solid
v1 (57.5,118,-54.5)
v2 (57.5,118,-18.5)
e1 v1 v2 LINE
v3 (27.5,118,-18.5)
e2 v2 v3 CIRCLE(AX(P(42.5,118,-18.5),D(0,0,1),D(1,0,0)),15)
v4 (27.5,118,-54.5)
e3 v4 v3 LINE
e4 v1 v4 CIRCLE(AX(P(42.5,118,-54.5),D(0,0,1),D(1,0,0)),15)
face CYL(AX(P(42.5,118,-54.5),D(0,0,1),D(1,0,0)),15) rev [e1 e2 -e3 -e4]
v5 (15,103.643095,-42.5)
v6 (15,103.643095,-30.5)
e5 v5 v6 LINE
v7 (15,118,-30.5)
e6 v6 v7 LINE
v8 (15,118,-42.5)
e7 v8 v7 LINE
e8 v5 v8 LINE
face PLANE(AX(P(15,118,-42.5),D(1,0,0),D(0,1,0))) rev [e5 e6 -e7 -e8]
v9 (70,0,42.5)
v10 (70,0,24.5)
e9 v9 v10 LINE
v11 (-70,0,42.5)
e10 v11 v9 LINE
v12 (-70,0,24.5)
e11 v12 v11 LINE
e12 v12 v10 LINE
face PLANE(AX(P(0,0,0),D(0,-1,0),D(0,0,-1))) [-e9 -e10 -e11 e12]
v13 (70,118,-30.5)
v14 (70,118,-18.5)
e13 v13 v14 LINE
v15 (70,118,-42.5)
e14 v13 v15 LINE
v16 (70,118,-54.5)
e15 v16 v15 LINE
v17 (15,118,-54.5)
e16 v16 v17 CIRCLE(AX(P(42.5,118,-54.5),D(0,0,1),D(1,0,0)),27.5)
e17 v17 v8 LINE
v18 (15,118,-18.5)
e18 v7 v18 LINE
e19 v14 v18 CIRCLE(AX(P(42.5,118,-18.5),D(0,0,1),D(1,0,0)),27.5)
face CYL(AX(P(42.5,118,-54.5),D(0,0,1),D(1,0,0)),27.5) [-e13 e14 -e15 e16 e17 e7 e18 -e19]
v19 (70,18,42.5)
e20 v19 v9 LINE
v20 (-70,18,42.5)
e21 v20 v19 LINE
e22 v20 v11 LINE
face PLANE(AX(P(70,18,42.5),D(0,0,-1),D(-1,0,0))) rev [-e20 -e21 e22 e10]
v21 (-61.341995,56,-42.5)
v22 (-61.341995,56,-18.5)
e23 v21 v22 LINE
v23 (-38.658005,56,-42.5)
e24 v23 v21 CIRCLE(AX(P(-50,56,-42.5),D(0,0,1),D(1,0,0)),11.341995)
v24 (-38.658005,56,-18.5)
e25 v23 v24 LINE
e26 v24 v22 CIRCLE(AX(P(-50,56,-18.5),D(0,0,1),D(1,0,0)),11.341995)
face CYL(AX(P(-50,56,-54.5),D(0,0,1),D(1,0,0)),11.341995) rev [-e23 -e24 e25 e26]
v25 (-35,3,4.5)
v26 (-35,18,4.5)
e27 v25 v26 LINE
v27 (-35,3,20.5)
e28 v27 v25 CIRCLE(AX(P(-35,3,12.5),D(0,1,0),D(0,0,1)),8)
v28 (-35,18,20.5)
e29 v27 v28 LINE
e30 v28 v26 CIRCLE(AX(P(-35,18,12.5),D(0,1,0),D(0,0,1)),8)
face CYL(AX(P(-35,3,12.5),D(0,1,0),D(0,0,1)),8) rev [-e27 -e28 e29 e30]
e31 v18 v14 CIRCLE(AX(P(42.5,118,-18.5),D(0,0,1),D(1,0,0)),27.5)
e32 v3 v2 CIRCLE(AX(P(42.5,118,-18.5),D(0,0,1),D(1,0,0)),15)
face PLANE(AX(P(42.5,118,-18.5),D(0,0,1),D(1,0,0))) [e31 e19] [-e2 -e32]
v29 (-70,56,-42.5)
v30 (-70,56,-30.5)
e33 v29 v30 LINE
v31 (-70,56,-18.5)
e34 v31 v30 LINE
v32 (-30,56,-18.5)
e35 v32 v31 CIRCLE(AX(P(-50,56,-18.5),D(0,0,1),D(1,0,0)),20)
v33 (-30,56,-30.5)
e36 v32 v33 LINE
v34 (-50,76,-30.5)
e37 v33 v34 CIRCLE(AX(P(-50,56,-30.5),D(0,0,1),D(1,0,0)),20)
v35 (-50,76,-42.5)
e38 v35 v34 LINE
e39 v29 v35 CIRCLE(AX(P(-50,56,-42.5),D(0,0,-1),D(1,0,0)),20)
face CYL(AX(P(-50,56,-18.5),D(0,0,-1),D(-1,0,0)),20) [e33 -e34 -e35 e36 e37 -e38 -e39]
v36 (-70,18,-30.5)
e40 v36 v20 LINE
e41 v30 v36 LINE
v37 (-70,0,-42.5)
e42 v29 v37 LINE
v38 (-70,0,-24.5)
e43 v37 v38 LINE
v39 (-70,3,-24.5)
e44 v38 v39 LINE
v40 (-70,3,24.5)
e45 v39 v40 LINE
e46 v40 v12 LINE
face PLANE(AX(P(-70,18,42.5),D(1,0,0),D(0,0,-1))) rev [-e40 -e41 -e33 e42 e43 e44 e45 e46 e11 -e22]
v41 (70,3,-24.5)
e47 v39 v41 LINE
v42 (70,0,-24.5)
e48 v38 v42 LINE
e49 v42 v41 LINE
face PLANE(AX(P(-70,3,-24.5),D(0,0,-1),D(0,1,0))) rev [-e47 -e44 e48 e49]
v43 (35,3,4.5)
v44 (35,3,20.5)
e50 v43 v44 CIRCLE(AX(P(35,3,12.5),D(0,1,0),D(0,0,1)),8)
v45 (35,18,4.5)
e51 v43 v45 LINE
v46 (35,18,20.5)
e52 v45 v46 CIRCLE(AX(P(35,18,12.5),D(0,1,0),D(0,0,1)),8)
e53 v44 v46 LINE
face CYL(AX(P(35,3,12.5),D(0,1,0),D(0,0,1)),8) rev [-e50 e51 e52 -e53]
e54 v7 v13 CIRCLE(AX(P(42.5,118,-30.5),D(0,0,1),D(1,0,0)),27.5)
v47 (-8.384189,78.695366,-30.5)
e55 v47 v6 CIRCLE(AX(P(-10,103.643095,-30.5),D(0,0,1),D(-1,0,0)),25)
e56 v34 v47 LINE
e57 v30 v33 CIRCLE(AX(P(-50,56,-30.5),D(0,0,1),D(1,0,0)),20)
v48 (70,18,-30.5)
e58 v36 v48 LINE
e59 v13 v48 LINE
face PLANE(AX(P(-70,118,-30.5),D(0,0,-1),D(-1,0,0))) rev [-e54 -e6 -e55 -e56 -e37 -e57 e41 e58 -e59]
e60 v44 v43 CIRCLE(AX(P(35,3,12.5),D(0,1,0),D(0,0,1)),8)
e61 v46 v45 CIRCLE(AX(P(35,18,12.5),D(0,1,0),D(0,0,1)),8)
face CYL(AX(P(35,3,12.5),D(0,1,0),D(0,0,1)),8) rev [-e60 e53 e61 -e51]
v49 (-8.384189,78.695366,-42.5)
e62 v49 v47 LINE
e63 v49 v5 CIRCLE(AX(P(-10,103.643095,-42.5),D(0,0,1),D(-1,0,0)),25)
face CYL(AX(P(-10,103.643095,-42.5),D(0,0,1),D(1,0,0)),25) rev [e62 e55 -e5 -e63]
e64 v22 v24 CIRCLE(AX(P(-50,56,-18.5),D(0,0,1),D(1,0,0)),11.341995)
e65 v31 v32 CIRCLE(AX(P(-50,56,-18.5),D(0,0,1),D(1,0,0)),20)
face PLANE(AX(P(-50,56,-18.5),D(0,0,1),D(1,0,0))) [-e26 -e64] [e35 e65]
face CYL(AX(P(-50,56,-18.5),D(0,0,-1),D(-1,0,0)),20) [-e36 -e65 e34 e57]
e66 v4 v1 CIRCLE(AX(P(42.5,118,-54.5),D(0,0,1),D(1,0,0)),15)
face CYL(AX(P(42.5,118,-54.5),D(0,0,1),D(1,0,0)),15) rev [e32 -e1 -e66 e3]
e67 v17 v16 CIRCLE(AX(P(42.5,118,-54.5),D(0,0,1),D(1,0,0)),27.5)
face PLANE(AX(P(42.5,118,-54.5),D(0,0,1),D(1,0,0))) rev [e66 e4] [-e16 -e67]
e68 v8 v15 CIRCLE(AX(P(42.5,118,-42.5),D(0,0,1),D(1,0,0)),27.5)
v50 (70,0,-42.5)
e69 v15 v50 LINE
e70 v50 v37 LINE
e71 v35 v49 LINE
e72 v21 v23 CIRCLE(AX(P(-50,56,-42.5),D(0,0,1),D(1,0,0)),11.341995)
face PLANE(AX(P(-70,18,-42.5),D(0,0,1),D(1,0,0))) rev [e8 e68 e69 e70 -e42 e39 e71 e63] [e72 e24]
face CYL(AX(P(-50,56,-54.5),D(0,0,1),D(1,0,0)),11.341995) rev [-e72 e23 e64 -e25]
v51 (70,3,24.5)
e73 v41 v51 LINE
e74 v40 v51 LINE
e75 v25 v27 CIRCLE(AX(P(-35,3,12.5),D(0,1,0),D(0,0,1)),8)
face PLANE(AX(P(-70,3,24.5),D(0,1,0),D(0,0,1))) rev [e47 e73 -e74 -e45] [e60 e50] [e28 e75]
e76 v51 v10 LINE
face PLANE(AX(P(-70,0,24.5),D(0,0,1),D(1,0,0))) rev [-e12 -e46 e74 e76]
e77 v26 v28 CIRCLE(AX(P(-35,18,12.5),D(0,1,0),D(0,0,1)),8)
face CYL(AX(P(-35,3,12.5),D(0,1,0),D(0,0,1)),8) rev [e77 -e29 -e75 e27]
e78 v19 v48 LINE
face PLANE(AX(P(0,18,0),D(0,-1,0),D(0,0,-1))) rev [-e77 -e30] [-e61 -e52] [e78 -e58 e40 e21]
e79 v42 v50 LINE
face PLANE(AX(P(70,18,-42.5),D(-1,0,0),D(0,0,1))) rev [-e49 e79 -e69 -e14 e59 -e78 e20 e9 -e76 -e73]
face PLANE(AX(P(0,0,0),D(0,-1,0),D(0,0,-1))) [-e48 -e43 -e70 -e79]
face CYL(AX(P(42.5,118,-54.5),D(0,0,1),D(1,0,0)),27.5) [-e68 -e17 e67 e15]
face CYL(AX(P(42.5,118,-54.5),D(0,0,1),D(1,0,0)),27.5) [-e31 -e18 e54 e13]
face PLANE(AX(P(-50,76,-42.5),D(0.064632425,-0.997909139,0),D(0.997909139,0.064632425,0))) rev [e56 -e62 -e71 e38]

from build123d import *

# Parameters (mm, degrees)
BASE_PLATE_SKETCH_W              = 140
BASE_PLATE_SKETCH_H              = 85
BASE_PLATE_85X140X18_DEPTH       = 18
UNDERSIDE_GROOVE_SKETCH_W        = 49
UNDERSIDE_GROOVE_SKETCH_H        = 3
UNDERSIDE_GROOVE_DEPTH           = 140
UPRIGHT_WALL_SKETCH_W            = 140
UPRIGHT_WALL_SKETCH_H            = 12
UPRIGHT_WALL_DEPTH               = 100
SMALL_LUG_40_SKETCH_R            = 20
SMALL_LUG_40_DEPTH               = 12
LARGE_LUG_55_SKETCH_R            = 27.5
LARGE_LUG_55_DEPTH               = 24
LARGE_START                      = 12
LARGE_LUG_EXTENSION_SKETCH_R     = 27.5
LARGE_LUG_EXTENSION_DEPTH        = 12
LUG_START                        = -12
LUG_RELIEF_CUT_DEPTH             = 12
LARGE_LUG_BORE_30_SKETCH_R       = 15
LARGE_LUG_BORE_30_DEPTH          = 36
SMALL_LUG_BORE_SKETCH_R          = 11.34199473
SMALL_LUG_BORE_DEPTH             = 36
BASE_MOUNTING_HOLE_1_16_SKETCH_R = 8
BASE_MOUNTING_HOLE_1_16_DEPTH    = 15
BASE_MOUNTING_HOLE_2_16_SKETCH_R = 8
BASE_MOUNTING_HOLE_2_16_DEPTH    = 15


with BuildPart() as part:
    # Base Plate Sketch → Base Plate 85x140x18 (new body)
    with BuildSketch(Plane(origin=(0, 0, 0), x_dir=(1, 0, 0), z_dir=(0, 1, 0))):
        Rectangle(BASE_PLATE_SKETCH_W, BASE_PLATE_SKETCH_H)
    extrude(amount=BASE_PLATE_85X140X18_DEPTH)

    # Underside Groove Sketch → Underside Groove (cut)
    with BuildSketch(Plane(origin=(70, 0, 0), x_dir=(0, 0, -1), z_dir=(1, 0, 0))):
        with Locations((0, 1.5)):
            Rectangle(UNDERSIDE_GROOVE_SKETCH_W, UNDERSIDE_GROOVE_SKETCH_H)
    extrude(amount=-UNDERSIDE_GROOVE_DEPTH, mode=Mode.SUBTRACT)

    # Upright Wall Sketch → Upright Wall (add)
    with BuildSketch(Plane(origin=(0, 18, 0), x_dir=(1, 0, 0), z_dir=(0, 1, 0))):
        with Locations((0, 36.5)):
            Rectangle(UPRIGHT_WALL_SKETCH_W, UPRIGHT_WALL_SKETCH_H)
    extrude(amount=UPRIGHT_WALL_DEPTH)

    # Small Lug Ø40 Sketch → Small Lug Ø40 (add)
    with BuildSketch(Plane.XY.offset(-30.5)):
        with Locations(Location((-50, 56, 0), (0, 0, 180))):
            Circle(SMALL_LUG_40_SKETCH_R)
    extrude(amount=SMALL_LUG_40_DEPTH)

    # Large Lug Ø55 Sketch → Large Lug Ø55 (add)
    with BuildSketch(Plane.XY.offset(-30.5)):
        with Locations((42.5, 118)):
            Circle(LARGE_LUG_55_SKETCH_R)
    extrude(amount=-LARGE_LUG_55_DEPTH)

    # Large Lug Extension Sketch → Large Lug Extension (add)
    with BuildSketch(Plane.XY.offset(-30.5).offset(LARGE_START)):
        with Locations((42.5, 118)):
            Circle(LARGE_LUG_EXTENSION_SKETCH_R)
    extrude(amount=-LARGE_LUG_EXTENSION_DEPTH)

    # Lug Relief Cut Sketch → Lug Relief Cut (cut)
    with BuildSketch(Plane.XY.offset(-30.5).offset(LUG_START)):
        with BuildLine():
            Line((15, 118), (15, 103.64309486))
            ThreePointArc((15, 103.64309486), (8.240000897, 86.546242306), (-8.384189381, 78.695366386))
            Line((-8.384189381, 78.695366386), (-50, 76))
            ThreePointArc((-50, 76), (-64.142135624, 70.142135624), (-70, 56))
            Line((-70, 56), (-70, 118))
            Line((-70, 118), (15, 118))
        make_face()
    extrude(amount=LUG_RELIEF_CUT_DEPTH, mode=Mode.SUBTRACT)

    # Large Lug Bore Ø30 Sketch → Large Lug Bore Ø30 (cut)
    with BuildSketch(Plane.XY.offset(-18.5)):
        with Locations((42.5, 118)):
            Circle(LARGE_LUG_BORE_30_SKETCH_R)
    extrude(amount=-LARGE_LUG_BORE_30_DEPTH, mode=Mode.SUBTRACT)

    # Small Lug Bore Sketch → Small Lug Bore (cut)
    with BuildSketch(Plane.XY.offset(-18.5)):
        with Locations((-50, 56)):
            Circle(SMALL_LUG_BORE_SKETCH_R)
    extrude(amount=-SMALL_LUG_BORE_DEPTH, mode=Mode.SUBTRACT)

    # Base Mounting Hole 1 Ø16 Sketch → Base Mounting Hole 1 Ø16 (cut)
    with BuildSketch(Plane(origin=(0, 18, 0), x_dir=(1, 0, 0), z_dir=(0, 1, 0))):
        with Locations(Location((-35, -12.5, 0), (0, 0, 270))):
            Circle(BASE_MOUNTING_HOLE_1_16_SKETCH_R)
    extrude(amount=-BASE_MOUNTING_HOLE_1_16_DEPTH, mode=Mode.SUBTRACT)

    # Base Mounting Hole 2 Ø16 Sketch → Base Mounting Hole 2 Ø16 (cut)
    with BuildSketch(Plane(origin=(0, 18, 0), x_dir=(1, 0, 0), z_dir=(0, 1, 0))):
        with Locations(Location((35, -12.5, 0), (0, 0, 270))):
            Circle(BASE_MOUNTING_HOLE_2_16_SKETCH_R)
    extrude(amount=-BASE_MOUNTING_HOLE_2_16_DEPTH, mode=Mode.SUBTRACT)


solid = part.part
